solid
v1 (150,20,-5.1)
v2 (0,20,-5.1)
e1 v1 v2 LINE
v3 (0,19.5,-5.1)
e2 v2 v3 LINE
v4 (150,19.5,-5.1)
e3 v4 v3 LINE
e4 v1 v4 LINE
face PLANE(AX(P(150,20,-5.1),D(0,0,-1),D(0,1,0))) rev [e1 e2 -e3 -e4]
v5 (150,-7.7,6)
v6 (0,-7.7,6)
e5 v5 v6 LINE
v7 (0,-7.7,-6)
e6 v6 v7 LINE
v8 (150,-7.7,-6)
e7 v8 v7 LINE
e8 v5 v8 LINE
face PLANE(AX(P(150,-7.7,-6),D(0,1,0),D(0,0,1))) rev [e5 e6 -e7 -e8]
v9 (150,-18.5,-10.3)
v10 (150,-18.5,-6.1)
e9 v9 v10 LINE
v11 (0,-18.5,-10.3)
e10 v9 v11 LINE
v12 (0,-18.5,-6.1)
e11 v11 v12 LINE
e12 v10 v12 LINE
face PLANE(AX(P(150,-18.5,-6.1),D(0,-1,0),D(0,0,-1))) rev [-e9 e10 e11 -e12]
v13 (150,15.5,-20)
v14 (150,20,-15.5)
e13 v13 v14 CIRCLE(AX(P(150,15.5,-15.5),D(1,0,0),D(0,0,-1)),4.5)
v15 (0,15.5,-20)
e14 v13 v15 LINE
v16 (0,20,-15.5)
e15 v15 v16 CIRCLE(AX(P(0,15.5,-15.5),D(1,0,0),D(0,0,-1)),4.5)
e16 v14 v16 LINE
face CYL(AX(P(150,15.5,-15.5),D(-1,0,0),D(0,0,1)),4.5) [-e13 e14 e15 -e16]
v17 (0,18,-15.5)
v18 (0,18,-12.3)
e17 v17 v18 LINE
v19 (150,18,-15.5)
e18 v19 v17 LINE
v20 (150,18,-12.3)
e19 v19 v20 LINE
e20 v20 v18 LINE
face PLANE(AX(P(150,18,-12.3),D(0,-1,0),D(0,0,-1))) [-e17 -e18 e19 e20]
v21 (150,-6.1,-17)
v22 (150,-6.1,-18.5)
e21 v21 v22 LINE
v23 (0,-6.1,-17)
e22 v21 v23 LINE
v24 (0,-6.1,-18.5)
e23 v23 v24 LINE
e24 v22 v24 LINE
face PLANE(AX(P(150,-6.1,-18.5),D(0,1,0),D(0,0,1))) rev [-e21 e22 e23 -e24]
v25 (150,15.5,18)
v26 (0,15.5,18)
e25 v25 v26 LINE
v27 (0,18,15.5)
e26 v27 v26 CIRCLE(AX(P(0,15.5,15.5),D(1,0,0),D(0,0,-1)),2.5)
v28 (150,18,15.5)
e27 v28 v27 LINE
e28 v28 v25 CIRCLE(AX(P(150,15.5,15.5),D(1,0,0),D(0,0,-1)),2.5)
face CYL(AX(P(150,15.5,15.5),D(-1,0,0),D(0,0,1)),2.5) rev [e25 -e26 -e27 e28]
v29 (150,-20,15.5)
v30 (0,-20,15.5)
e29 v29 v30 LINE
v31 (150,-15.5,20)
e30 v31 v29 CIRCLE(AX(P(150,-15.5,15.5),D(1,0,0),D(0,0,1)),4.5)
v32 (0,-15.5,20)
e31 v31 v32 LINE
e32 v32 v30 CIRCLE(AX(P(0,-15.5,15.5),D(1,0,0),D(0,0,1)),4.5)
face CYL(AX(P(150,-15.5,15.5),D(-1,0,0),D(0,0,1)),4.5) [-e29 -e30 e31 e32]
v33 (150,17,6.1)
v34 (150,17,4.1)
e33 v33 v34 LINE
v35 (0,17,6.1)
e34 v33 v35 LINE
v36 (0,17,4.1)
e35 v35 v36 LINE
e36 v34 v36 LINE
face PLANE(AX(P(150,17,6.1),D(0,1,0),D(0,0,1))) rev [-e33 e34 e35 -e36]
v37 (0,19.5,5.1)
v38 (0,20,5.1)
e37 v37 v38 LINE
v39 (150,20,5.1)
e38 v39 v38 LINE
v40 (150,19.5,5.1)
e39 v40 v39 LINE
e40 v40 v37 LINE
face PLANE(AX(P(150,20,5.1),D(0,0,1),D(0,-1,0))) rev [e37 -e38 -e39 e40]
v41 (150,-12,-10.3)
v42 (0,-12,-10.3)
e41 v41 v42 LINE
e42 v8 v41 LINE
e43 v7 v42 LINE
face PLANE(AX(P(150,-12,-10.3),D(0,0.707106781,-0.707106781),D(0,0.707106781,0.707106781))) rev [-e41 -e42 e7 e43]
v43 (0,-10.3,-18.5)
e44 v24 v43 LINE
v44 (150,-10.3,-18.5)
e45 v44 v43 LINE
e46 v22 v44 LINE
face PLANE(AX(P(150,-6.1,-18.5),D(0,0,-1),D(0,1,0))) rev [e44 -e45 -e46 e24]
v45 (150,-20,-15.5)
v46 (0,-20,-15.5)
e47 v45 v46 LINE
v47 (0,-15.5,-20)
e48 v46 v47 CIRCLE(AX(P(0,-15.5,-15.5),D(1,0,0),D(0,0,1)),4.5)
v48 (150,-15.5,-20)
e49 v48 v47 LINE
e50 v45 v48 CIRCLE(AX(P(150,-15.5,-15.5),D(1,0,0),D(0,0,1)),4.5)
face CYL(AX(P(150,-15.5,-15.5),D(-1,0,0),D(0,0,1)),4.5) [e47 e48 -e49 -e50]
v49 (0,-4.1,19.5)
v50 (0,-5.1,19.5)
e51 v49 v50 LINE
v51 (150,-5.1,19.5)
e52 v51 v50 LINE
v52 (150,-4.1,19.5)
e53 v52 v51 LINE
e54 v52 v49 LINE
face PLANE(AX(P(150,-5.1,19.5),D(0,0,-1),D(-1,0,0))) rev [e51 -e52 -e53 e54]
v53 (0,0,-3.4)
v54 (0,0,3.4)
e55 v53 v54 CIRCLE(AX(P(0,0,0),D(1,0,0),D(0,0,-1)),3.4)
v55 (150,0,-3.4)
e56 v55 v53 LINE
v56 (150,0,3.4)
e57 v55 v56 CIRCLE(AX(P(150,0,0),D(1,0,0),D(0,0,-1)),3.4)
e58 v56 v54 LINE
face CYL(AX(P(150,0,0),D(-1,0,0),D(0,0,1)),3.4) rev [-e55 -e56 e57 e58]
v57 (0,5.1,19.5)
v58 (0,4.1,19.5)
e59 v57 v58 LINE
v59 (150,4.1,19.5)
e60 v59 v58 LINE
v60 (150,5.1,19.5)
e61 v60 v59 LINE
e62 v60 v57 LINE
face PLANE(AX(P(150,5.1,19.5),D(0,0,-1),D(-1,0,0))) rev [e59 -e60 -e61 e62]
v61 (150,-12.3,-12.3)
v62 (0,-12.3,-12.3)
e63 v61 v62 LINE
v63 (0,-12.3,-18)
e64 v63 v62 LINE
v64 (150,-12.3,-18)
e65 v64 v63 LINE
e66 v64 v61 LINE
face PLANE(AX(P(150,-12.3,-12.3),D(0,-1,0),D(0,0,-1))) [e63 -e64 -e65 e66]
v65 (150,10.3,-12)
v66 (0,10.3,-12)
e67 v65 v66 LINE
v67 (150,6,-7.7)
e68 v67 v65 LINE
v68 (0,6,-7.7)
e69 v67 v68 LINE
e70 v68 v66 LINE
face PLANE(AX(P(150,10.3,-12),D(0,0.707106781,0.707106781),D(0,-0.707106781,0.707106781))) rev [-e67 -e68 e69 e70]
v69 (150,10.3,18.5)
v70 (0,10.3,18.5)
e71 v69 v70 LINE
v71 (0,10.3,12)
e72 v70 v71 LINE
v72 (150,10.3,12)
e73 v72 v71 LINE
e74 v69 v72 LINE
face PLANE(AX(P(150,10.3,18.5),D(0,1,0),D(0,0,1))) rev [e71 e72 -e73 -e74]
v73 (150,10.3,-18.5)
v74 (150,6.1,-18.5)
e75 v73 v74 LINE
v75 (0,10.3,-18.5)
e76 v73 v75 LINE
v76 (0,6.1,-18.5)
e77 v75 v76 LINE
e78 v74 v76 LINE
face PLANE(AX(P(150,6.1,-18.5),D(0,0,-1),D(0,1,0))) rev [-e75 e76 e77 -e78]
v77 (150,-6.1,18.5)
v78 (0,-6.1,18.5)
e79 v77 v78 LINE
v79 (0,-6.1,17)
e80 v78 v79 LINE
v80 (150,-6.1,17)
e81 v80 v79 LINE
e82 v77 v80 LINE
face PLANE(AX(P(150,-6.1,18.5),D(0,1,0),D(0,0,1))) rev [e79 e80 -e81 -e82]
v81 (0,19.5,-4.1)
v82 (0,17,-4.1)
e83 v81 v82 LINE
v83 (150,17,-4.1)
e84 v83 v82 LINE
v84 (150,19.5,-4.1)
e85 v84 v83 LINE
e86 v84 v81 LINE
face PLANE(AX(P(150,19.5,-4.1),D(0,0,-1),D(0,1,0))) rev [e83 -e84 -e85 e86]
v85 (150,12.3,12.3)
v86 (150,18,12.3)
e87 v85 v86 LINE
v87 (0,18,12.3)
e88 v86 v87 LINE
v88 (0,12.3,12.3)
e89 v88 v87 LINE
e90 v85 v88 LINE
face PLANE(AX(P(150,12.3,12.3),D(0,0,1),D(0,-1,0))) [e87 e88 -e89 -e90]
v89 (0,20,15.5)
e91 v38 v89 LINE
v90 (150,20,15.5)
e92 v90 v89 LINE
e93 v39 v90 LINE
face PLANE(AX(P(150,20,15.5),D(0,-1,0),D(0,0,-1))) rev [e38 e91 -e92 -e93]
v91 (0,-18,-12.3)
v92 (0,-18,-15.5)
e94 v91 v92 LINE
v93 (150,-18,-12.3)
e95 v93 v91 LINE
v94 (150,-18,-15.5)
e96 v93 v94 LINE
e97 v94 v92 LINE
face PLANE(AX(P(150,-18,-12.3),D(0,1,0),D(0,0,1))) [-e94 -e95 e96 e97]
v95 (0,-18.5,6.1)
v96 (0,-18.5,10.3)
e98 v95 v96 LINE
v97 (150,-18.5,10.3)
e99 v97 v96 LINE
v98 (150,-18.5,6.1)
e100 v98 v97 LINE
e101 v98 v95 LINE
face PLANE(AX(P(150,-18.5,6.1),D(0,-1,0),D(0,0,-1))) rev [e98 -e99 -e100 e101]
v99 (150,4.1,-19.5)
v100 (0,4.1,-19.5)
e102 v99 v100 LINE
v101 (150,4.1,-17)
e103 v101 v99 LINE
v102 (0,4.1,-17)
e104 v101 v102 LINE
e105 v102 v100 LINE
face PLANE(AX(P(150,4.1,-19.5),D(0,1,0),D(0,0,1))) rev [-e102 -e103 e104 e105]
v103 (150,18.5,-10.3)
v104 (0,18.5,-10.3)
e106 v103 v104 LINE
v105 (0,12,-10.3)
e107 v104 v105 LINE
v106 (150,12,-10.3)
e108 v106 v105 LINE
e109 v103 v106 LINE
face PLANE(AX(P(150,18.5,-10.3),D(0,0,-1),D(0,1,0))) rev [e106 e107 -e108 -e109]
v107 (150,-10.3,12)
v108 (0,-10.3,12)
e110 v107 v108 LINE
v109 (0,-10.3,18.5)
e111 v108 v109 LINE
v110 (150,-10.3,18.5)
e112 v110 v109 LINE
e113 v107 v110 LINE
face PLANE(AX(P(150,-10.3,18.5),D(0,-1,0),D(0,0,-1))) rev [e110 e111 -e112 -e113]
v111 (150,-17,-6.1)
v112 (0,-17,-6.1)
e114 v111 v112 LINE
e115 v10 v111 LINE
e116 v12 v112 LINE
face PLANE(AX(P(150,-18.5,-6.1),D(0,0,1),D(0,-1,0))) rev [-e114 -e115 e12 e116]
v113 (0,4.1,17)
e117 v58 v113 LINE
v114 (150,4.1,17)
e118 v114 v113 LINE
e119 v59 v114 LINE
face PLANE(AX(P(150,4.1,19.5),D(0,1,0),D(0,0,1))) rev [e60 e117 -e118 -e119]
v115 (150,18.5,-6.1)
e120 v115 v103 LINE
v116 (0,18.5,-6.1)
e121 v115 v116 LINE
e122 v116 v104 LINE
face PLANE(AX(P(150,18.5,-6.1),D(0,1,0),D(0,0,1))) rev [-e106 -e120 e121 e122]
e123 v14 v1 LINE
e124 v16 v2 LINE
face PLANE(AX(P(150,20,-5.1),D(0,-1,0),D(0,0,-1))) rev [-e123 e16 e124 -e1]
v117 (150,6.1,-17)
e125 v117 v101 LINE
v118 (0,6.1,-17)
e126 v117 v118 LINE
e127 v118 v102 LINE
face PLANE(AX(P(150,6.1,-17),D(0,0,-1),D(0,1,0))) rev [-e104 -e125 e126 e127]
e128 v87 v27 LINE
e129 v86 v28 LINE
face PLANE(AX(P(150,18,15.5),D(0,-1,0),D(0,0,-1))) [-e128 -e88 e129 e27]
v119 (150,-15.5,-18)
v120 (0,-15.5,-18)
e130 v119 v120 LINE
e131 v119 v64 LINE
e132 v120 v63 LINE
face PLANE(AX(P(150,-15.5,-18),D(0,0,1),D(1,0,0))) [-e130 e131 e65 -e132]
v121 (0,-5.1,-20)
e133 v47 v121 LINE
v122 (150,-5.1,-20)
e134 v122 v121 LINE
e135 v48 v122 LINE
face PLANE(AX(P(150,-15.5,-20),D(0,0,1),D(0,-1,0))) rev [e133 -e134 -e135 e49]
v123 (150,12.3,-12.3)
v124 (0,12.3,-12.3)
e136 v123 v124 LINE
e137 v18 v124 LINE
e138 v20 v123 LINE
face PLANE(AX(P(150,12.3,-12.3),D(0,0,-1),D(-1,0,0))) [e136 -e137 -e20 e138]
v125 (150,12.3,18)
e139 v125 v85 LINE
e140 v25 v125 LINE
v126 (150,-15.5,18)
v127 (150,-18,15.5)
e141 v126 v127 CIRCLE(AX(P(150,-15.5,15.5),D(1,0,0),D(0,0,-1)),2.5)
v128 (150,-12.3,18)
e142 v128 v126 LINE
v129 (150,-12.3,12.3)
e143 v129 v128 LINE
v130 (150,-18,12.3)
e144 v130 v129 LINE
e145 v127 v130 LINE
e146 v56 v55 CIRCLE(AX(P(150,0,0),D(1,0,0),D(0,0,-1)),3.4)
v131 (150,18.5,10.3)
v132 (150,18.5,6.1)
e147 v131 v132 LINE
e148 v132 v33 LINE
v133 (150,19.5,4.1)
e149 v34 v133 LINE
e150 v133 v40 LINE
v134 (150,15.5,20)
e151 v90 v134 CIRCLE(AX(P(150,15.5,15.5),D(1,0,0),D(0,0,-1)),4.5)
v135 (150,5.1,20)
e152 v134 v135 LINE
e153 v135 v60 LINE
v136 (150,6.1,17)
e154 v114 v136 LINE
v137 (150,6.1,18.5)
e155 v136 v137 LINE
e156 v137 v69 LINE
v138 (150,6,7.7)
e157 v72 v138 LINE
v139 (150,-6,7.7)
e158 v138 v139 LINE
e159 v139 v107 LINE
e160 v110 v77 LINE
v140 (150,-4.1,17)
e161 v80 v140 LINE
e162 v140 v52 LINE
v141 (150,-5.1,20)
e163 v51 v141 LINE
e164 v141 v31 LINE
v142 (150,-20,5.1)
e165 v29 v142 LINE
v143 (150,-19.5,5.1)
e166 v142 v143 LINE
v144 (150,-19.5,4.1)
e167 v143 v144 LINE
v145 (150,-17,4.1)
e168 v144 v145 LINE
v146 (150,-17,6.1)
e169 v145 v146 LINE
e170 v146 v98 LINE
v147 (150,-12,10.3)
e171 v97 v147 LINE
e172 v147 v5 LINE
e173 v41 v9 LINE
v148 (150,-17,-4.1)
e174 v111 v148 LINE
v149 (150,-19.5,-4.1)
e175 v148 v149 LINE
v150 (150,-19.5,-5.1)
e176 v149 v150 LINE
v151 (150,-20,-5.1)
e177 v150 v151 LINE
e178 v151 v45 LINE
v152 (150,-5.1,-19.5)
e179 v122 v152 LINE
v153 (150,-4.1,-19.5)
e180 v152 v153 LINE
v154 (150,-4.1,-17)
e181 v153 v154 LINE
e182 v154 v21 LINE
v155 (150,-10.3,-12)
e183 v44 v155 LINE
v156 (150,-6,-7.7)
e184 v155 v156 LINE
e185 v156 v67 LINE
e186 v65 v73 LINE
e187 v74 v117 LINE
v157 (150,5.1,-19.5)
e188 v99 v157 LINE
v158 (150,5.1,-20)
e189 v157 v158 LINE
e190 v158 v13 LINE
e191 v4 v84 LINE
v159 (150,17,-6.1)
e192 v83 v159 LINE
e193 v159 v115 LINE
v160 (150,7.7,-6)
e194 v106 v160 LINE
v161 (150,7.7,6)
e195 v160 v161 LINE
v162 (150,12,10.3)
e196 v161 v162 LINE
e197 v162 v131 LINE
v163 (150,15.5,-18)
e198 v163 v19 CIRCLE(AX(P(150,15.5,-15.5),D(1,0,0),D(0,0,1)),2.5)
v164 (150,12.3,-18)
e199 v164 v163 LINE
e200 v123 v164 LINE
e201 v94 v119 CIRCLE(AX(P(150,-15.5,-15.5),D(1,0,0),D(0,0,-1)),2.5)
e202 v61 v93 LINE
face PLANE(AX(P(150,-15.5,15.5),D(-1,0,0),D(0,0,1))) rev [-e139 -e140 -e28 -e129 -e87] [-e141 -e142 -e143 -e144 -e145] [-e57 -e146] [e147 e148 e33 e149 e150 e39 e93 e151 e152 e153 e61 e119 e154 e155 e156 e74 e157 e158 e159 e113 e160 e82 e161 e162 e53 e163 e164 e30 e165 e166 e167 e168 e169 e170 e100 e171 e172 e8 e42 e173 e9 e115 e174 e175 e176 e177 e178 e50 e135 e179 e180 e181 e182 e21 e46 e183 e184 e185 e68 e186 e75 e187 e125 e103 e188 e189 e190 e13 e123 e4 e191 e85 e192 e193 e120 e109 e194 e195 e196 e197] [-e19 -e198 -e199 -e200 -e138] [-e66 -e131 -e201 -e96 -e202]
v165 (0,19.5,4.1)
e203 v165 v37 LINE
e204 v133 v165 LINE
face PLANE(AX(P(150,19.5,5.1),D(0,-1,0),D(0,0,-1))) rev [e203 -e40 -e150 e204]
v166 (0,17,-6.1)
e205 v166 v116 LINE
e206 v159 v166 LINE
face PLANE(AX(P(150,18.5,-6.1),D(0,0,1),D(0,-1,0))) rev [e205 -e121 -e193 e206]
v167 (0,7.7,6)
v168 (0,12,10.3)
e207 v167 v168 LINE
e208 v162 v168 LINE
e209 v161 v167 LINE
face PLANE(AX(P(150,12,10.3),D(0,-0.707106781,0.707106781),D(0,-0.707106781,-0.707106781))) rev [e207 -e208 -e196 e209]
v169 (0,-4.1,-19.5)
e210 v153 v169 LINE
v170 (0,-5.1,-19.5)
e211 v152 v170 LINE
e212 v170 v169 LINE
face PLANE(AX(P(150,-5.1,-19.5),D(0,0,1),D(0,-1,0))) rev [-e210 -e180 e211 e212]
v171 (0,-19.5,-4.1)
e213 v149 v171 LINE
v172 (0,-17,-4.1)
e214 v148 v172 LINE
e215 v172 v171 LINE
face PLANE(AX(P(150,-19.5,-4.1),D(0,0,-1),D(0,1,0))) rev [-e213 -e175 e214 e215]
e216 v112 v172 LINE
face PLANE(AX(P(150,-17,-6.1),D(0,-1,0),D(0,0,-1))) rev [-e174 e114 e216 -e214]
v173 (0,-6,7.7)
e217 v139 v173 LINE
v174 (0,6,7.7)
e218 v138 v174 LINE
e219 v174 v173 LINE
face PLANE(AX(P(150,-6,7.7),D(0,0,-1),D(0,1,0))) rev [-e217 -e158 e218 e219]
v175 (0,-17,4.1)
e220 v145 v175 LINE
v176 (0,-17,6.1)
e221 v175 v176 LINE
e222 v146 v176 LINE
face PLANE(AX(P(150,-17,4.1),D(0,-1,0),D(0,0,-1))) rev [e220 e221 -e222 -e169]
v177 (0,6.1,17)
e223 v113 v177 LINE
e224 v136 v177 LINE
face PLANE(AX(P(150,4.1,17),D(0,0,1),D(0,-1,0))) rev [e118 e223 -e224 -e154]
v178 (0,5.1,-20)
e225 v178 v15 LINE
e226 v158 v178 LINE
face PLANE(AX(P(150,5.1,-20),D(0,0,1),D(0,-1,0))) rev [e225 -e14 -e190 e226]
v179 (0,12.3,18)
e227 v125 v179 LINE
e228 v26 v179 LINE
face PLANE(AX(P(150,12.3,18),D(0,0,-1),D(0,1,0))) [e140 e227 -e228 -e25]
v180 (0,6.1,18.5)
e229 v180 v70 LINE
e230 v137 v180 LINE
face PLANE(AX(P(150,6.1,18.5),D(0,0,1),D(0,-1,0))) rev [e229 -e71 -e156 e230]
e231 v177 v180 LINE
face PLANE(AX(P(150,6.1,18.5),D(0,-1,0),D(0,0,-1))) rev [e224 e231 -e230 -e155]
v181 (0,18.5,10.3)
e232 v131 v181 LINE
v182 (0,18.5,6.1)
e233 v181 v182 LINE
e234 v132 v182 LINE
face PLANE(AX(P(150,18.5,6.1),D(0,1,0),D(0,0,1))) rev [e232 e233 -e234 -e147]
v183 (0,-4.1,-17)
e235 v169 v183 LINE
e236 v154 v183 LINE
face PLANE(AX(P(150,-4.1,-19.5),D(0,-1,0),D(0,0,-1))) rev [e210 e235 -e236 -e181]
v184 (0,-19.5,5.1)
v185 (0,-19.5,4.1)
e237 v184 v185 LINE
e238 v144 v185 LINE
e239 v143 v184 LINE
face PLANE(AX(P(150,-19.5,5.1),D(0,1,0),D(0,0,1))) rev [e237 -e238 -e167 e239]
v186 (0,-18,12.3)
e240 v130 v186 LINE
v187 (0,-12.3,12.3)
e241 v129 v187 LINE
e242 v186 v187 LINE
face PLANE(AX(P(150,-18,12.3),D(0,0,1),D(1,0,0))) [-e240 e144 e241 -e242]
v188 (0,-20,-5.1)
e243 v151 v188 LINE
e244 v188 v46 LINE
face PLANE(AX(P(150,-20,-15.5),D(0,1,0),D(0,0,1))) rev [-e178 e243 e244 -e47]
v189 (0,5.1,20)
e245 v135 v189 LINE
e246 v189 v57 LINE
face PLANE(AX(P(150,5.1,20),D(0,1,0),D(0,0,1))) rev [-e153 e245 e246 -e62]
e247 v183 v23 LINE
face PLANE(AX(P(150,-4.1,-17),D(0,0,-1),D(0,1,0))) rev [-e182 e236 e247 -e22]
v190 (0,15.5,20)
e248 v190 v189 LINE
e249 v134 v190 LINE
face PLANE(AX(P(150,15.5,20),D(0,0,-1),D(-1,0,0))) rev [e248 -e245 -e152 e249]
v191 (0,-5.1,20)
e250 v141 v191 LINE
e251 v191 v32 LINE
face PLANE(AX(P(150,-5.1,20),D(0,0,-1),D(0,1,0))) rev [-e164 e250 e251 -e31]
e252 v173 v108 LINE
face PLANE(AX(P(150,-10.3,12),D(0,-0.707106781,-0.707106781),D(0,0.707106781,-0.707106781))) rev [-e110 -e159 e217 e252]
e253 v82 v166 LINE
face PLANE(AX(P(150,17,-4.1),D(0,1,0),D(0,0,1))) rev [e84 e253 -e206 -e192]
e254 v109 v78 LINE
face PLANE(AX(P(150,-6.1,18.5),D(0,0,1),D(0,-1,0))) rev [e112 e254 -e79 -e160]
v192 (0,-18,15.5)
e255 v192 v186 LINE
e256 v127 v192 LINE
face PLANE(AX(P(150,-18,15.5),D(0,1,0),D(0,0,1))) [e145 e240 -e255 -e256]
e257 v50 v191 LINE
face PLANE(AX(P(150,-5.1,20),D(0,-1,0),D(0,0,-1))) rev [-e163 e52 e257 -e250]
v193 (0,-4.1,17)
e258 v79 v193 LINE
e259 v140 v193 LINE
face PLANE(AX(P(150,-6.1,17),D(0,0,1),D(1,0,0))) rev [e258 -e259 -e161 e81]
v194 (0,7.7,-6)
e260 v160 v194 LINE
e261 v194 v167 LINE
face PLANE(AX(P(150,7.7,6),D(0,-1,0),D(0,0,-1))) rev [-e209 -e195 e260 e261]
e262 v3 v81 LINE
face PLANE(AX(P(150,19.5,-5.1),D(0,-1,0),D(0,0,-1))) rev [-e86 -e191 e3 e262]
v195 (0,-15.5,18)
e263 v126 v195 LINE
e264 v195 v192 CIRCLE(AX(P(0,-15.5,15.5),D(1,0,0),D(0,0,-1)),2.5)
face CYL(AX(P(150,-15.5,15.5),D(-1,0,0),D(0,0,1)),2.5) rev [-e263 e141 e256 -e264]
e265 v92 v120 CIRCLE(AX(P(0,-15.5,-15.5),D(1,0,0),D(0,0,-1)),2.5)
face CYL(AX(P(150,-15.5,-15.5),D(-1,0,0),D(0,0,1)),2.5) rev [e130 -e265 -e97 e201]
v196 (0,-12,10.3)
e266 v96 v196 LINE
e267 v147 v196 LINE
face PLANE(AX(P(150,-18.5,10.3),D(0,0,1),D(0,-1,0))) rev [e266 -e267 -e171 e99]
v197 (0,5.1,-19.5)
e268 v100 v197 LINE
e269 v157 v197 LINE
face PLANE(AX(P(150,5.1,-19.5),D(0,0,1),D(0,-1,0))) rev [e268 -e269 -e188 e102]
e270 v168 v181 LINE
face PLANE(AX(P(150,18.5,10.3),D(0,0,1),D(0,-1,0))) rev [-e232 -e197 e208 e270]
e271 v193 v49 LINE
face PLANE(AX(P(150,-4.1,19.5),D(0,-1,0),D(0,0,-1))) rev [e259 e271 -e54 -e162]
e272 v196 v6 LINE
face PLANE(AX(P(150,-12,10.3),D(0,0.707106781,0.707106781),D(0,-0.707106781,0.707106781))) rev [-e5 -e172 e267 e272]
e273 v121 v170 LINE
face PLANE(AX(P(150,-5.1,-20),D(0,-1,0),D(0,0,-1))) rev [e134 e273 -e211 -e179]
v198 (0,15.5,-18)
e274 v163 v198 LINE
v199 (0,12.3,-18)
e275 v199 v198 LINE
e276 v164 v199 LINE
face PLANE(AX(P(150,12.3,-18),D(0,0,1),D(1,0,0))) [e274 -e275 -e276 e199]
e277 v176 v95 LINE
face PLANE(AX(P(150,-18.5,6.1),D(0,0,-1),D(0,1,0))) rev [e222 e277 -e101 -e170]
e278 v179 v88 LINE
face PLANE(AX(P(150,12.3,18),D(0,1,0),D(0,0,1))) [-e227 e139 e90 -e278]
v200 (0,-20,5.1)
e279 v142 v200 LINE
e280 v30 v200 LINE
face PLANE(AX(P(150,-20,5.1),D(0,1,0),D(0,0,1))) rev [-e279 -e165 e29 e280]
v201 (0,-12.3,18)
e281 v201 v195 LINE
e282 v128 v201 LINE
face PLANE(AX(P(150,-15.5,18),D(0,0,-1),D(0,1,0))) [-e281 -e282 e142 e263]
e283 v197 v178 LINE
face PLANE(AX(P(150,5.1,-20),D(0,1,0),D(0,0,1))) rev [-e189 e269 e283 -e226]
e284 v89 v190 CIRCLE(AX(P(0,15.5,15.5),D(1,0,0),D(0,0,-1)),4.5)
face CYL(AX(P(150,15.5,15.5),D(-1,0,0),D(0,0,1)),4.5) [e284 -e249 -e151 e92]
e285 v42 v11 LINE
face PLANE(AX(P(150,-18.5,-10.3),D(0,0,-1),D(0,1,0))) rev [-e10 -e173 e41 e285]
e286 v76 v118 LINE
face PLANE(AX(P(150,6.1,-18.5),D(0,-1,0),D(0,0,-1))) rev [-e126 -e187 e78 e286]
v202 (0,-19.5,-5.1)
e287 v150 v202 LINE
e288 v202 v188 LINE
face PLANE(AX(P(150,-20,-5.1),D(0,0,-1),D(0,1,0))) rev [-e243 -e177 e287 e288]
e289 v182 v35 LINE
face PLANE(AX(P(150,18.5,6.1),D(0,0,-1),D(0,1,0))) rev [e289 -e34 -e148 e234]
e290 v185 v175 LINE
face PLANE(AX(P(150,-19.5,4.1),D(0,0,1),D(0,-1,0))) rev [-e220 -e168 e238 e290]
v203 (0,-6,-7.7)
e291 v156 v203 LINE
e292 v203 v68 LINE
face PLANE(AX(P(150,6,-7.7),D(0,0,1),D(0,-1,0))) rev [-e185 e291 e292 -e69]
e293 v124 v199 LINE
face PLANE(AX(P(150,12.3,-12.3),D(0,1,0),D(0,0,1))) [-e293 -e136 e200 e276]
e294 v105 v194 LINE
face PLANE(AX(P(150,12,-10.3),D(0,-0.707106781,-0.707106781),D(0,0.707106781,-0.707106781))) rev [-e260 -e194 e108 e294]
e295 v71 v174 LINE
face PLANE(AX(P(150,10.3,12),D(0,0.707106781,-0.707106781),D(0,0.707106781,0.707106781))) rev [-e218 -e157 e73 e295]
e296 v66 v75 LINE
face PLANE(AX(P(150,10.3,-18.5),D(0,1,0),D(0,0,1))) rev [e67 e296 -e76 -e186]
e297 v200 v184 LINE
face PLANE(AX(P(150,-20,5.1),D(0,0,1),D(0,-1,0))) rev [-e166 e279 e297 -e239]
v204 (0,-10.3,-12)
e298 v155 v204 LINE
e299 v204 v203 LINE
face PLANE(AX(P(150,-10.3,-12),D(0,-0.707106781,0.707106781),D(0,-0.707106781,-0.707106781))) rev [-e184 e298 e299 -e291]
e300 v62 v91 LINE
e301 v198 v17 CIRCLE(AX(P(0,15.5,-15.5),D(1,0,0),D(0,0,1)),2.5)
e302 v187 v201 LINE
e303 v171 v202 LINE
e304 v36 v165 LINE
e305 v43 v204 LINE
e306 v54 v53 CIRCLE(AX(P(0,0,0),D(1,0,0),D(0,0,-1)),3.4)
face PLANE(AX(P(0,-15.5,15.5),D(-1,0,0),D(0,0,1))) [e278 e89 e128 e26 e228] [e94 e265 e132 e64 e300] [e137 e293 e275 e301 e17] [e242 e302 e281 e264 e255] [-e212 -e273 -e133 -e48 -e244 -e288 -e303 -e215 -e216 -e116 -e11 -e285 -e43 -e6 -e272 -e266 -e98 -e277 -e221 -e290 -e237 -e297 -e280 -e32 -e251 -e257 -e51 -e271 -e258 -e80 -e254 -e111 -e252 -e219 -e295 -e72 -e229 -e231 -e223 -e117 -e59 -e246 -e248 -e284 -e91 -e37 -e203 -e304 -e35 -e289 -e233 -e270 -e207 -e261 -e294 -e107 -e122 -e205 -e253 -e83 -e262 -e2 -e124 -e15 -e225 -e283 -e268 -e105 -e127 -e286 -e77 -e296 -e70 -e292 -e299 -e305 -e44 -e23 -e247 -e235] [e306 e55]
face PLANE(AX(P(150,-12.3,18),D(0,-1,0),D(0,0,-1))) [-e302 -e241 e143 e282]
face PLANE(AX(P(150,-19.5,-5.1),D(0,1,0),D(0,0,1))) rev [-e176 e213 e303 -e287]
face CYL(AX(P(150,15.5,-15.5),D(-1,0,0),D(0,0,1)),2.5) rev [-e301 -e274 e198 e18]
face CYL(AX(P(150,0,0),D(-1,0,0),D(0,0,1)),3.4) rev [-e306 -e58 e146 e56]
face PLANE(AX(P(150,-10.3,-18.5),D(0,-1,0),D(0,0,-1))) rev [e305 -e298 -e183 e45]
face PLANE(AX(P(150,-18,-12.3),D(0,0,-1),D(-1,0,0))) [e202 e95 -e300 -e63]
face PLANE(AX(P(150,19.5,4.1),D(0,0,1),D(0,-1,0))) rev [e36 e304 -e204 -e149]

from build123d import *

# Parameters (mm, degrees)
SKETCH1_R                                = 3.4
ALUMINUM_PROFILE_40_X_40B_X_R4_5_1_DEPTH = 150


with BuildPart() as part:
    # Sketch1 → Aluminum profile 40 X 40B X R4.5(1) (new body)
    with BuildSketch(Plane.YZ):
        with BuildLine():
            Line((-5.1, 20), (-5.1, 19.5))
            Line((-5.1, 19.5), (-4.1, 19.5))
            Line((-4.1, 19.5), (-4.1, 17))
            Line((-4.1, 17), (-6.1, 17))
            Line((-6.1, 17), (-6.1, 18.5))
            Line((-6.1, 18.5), (-10.3, 18.5))
            Line((-10.3, 18.5), (-10.3, 12))
            Line((-10.3, 12), (-6, 7.7))
            Line((-6, 7.7), (6, 7.7))
            Line((6, 7.7), (10.3, 12))
            Line((10.3, 12), (10.3, 18.5))
            Line((10.3, 18.5), (6.1, 18.5))
            Line((6.1, 18.5), (6.1, 17))
            Line((6.1, 17), (4.1, 17))
            Line((4.1, 17), (4.1, 19.5))
            Line((4.1, 19.5), (5.1, 19.5))
            Line((5.1, 19.5), (5.1, 20))
            Line((5.1, 20), (15.5, 20))
            ThreePointArc((15.5, 20), (18.681980515, 18.681980515), (20, 15.5))
            Line((20, 15.5), (20, 5.1))
            Line((20, 5.1), (19.5, 5.1))
            Line((19.5, 5.1), (19.5, 4.1))
            Line((19.5, 4.1), (17, 4.1))
            Line((17, 4.1), (17, 6.1))
            Line((17, 6.1), (18.5, 6.1))
            Line((18.5, 6.1), (18.5, 10.3))
            Line((18.5, 10.3), (12, 10.3))
            Line((12, 10.3), (7.7, 6))
            Line((7.7, 6), (7.7, -6))
            Line((7.7, -6), (12, -10.3))
            Line((12, -10.3), (18.5, -10.3))
            Line((18.5, -10.3), (18.5, -6.1))
            Line((18.5, -6.1), (17, -6.1))
            Line((17, -6.1), (17, -4.1))
            Line((17, -4.1), (19.5, -4.1))
            Line((19.5, -4.1), (19.5, -5.1))
            Line((19.5, -5.1), (20, -5.1))
            Line((20, -5.1), (20, -15.5))
            ThreePointArc((20, -15.5), (18.681980515, -18.681980515), (15.5, -20))
            Line((15.5, -20), (5.1, -20))
            Line((5.1, -20), (5.1, -19.5))
            Line((5.1, -19.5), (4.1, -19.5))
            Line((4.1, -19.5), (4.1, -17))
            Line((4.1, -17), (6.1, -17))
            Line((6.1, -17), (6.1, -18.5))
            Line((6.1, -18.5), (10.3, -18.5))
            Line((10.3, -18.5), (10.3, -12))
            Line((10.3, -12), (6, -7.7))
            Line((6, -7.7), (-6, -7.7))
            Line((-6, -7.7), (-10.3, -12))
            Line((-10.3, -12), (-10.3, -18.5))
            Line((-10.3, -18.5), (-6.1, -18.5))
            Line((-6.1, -18.5), (-6.1, -17))
            Line((-6.1, -17), (-4.1, -17))
            Line((-4.1, -17), (-4.1, -19.5))
            Line((-4.1, -19.5), (-5.1, -19.5))
            Line((-5.1, -19.5), (-5.1, -20))
            Line((-5.1, -20), (-15.5, -20))
            ThreePointArc((-15.5, -20), (-18.681980515, -18.681980515), (-20, -15.5))
            Line((-20, -15.5), (-20, -5.1))
            Line((-20, -5.1), (-19.5, -5.1))
            Line((-19.5, -5.1), (-19.5, -4.1))
            Line((-19.5, -4.1), (-17, -4.1))
            Line((-17, -4.1), (-17, -6.1))
            Line((-17, -6.1), (-18.5, -6.1))
            Line((-18.5, -6.1), (-18.5, -10.3))
            Line((-18.5, -10.3), (-12, -10.3))
            Line((-12, -10.3), (-7.7, -6))
            Line((-7.7, -6), (-7.7, 6))
            Line((-7.7, 6), (-12, 10.3))
            Line((-12, 10.3), (-18.5, 10.3))
            Line((-18.5, 10.3), (-18.5, 6.1))
            Line((-18.5, 6.1), (-17, 6.1))
            Line((-17, 6.1), (-17, 4.1))
            Line((-17, 4.1), (-19.5, 4.1))
            Line((-19.5, 4.1), (-19.5, 5.1))
            Line((-19.5, 5.1), (-20, 5.1))
            Line((-20, 5.1), (-20, 15.5))
            ThreePointArc((-20, 15.5), (-18.681980515, 18.681980515), (-15.5, 20))
            Line((-15.5, 20), (-5.1, 20))
        make_face()
        Circle(SKETCH1_R, mode=Mode.SUBTRACT)
        with BuildLine():
            Line((12.3, 18), (15.5, 18))
            ThreePointArc((15.5, 18), (17.267766953, 17.267766953), (18, 15.5))
            Line((18, 15.5), (18, 12.3))
            Line((18, 12.3), (12.3, 12.3))
            Line((12.3, 12.3), (12.3, 18))
        make_face(mode=Mode.SUBTRACT)
        with BuildLine():
            Line((-15.5, 18), (-12.3, 18))
            Line((-12.3, 18), (-12.3, 12.3))
            Line((-12.3, 12.3), (-18, 12.3))
            Line((-18, 12.3), (-18, 15.5))
            ThreePointArc((-18, 15.5), (-17.267766953, 17.267766953), (-15.5, 18))
        make_face(mode=Mode.SUBTRACT)
        with BuildLine():
            Line((-18, -12.3), (-12.3, -12.3))
            Line((-12.3, -12.3), (-12.3, -18))
            Line((-12.3, -18), (-15.5, -18))
            ThreePointArc((-15.5, -18), (-17.267766953, -17.267766953), (-18, -15.5))
            Line((-18, -15.5), (-18, -12.3))
        make_face(mode=Mode.SUBTRACT)
        with BuildLine():
            Line((12.3, -12.3), (18, -12.3))
            Line((18, -12.3), (18, -15.5))
            ThreePointArc((18, -15.5), (17.267766953, -17.267766953), (15.5, -18))
            Line((15.5, -18), (12.3, -18))
            Line((12.3, -18), (12.3, -12.3))
        make_face(mode=Mode.SUBTRACT)
    extrude(amount=ALUMINUM_PROFILE_40_X_40B_X_R4_5_1_DEPTH)


solid = part.part
